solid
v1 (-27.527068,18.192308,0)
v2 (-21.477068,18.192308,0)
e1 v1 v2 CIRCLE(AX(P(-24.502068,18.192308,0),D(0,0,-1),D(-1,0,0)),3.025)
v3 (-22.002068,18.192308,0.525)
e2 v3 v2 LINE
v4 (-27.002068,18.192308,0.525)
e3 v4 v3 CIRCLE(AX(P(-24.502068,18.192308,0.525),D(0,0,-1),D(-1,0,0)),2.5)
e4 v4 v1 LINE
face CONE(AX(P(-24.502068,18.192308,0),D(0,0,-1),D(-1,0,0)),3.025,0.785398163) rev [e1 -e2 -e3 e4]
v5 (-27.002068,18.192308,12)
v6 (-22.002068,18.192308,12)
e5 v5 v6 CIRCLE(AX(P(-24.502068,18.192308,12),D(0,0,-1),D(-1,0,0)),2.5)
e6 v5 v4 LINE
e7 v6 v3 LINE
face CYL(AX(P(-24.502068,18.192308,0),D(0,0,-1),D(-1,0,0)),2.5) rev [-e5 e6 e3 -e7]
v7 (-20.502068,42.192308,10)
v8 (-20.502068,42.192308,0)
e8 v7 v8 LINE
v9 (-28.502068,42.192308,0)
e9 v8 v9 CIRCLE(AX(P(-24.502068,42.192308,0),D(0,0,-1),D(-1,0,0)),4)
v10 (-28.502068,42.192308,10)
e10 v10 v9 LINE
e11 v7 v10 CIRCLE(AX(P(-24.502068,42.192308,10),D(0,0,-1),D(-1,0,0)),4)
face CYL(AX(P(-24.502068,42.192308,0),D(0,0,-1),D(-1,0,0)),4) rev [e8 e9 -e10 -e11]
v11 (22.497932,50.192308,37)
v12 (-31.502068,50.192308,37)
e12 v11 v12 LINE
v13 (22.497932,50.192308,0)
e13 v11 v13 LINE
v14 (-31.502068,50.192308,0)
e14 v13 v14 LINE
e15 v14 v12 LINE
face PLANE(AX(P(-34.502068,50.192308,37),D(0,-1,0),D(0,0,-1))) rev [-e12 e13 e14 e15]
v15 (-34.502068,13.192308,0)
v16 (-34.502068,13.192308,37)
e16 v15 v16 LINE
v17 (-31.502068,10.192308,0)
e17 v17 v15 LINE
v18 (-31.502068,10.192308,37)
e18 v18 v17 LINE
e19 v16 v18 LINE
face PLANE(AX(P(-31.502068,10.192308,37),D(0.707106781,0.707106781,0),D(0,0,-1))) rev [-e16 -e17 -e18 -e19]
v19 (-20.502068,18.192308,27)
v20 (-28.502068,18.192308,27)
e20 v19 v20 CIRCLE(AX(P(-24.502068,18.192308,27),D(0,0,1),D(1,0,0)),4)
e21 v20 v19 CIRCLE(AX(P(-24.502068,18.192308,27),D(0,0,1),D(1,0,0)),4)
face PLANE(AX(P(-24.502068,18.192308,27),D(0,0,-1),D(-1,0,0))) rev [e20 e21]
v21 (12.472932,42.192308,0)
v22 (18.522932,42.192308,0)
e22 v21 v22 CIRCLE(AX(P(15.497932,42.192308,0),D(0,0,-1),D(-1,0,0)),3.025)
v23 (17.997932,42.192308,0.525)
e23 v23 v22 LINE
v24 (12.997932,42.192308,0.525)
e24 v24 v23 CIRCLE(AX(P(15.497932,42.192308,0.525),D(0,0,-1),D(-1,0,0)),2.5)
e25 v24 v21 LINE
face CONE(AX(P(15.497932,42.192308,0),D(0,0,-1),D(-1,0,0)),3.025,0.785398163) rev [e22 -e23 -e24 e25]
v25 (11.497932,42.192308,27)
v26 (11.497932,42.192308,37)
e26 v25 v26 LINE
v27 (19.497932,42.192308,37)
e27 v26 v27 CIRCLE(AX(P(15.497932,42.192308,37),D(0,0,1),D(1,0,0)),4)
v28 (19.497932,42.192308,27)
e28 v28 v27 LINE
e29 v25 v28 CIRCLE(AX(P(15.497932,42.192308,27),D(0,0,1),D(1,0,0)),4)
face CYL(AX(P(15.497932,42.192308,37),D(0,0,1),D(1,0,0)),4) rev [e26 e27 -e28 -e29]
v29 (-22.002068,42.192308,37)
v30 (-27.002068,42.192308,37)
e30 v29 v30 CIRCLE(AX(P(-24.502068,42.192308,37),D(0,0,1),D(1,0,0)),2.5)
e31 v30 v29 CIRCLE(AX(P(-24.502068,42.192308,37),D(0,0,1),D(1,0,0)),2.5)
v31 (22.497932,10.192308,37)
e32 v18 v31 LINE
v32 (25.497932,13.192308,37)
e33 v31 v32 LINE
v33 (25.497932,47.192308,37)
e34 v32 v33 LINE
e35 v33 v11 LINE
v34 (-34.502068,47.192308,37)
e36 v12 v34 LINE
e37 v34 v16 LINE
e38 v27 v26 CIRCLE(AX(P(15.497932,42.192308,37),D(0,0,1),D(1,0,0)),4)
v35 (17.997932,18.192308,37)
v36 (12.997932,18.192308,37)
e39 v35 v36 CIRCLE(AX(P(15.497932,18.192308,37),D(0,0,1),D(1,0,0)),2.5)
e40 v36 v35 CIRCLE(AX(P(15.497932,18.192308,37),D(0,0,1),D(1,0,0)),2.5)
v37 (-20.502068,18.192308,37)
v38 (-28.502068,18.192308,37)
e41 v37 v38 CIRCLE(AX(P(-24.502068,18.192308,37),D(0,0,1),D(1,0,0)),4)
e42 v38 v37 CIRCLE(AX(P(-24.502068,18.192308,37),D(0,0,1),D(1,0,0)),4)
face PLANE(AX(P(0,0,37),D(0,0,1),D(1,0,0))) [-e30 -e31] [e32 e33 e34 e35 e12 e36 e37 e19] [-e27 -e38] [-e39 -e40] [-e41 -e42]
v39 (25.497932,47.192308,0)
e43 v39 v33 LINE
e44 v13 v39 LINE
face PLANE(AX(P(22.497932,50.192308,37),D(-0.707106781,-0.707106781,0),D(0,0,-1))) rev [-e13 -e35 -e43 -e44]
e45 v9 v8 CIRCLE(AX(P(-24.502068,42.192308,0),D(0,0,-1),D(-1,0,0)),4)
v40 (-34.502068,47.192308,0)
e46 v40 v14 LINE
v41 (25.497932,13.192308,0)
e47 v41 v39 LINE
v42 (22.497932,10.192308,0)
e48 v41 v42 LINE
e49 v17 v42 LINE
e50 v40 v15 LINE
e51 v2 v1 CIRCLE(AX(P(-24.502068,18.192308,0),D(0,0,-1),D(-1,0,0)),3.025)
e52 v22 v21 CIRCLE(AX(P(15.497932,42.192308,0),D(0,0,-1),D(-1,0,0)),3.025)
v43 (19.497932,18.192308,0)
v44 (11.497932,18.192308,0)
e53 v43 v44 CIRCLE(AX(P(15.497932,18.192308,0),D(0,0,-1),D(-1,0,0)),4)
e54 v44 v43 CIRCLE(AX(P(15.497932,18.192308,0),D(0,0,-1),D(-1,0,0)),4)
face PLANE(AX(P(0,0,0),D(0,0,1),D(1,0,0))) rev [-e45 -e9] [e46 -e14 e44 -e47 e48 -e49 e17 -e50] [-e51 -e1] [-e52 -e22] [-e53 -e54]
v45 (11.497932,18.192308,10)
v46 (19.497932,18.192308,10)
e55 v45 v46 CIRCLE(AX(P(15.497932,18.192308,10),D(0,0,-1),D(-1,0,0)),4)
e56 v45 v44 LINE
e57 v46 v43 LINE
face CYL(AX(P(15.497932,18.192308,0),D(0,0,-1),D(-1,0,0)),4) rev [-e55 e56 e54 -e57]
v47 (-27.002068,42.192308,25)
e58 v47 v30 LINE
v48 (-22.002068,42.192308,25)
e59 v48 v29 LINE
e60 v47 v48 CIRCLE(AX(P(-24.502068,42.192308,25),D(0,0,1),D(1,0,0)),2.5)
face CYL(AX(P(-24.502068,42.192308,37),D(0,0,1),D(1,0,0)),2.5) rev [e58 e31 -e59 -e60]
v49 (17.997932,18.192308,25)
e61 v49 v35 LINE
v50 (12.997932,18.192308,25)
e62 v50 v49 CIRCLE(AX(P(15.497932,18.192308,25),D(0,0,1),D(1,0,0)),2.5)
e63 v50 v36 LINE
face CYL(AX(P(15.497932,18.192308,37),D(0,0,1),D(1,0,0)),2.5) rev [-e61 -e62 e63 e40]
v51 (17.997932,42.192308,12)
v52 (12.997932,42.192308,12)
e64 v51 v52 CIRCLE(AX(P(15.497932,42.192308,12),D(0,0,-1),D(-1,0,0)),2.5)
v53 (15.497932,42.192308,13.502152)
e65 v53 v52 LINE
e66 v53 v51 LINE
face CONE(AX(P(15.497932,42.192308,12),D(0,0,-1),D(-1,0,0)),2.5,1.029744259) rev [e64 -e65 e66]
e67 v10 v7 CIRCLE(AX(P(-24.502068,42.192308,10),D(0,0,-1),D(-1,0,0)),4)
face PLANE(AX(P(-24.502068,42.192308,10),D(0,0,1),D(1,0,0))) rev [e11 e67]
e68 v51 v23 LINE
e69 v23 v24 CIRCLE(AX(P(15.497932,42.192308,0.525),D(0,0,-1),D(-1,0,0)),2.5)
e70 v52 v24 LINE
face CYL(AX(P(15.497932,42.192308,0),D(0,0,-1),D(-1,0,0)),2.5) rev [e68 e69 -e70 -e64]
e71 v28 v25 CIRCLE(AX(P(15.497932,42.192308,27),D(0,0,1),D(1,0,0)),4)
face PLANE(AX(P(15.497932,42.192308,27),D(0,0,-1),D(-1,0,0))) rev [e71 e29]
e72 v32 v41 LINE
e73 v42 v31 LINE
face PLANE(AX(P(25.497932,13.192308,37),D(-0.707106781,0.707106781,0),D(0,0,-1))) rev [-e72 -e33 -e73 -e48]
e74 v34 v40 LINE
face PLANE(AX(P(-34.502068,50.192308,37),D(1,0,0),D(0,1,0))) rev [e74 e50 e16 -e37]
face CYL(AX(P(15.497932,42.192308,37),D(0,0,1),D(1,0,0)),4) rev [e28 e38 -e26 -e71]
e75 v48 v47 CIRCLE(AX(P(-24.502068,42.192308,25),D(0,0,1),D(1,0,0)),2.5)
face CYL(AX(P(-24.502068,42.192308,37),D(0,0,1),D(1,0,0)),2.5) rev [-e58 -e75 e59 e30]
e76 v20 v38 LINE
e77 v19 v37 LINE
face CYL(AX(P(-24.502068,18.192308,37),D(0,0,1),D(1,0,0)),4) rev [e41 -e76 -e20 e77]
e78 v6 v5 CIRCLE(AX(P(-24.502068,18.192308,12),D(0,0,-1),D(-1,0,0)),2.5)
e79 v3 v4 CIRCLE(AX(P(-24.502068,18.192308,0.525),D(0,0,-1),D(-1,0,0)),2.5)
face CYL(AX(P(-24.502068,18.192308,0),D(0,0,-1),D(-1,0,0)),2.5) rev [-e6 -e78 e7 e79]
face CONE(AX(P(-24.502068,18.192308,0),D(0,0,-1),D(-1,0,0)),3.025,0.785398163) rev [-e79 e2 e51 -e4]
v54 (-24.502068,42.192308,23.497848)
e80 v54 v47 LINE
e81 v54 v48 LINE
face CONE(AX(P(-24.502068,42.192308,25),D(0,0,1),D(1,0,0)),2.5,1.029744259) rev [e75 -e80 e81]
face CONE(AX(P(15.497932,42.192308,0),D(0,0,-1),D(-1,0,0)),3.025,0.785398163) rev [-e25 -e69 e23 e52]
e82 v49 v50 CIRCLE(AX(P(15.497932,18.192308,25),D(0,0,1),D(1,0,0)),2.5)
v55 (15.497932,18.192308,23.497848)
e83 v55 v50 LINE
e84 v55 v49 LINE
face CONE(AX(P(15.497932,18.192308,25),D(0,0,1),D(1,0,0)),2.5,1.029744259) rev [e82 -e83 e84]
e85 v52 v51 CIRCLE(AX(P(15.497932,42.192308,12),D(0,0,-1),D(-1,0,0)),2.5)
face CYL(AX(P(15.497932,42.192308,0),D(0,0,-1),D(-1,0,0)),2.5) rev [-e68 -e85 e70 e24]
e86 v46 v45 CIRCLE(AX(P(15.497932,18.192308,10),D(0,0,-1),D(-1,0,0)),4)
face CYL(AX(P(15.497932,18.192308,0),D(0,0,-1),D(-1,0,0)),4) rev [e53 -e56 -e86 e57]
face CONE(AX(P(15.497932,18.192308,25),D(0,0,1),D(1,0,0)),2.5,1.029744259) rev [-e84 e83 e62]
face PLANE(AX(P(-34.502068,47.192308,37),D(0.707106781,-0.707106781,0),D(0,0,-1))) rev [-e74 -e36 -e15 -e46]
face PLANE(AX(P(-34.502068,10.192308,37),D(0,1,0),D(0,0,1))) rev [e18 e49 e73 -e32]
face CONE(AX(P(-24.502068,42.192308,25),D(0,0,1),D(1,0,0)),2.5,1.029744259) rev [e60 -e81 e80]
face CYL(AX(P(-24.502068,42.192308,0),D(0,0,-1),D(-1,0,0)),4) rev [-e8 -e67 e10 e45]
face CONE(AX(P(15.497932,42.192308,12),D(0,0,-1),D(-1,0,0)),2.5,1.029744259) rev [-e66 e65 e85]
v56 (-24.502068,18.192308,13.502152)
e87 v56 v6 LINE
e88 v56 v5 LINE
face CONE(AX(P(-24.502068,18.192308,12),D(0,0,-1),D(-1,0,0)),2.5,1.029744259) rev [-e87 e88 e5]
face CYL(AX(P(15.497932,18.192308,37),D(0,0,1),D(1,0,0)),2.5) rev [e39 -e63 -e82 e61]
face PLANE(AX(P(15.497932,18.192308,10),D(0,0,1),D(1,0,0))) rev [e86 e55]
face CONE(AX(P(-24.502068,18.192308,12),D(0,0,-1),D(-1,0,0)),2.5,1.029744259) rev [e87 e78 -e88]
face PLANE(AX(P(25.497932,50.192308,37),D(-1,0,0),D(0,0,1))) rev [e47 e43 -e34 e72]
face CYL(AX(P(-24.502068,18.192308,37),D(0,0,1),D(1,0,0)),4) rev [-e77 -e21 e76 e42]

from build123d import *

# Parameters (mm, degrees)
SKETCH1_W                   = 60
SKETCH1_H                   = 40
BOSS_EXTRUDE1_DEPTH         = 37
CHAMFER1_SIZE               = 3
M6_TAPPED_HOLE1_D           = 5
M6_TAPPED_HOLE1_DEPTH       = 12
M6_TAPPED_HOLE1_TIP         = 1.502151548
HOLE1_D                     = 8
HOLE1_DEPTH                 = 10
HOLE2_D                     = 8
HOLE2_DEPTH                 = 10
M6_TAPPED_HOLE2_D           = 5
M6_TAPPED_HOLE2_DEPTH       = 12
M6_TAPPED_HOLE2_CSINK_D     = 6.05
M6_TAPPED_HOLE2_CSINK_ANGLE = 90
M6_TAPPED_HOLE2_TIP         = 1.502151548


with BuildPart() as part:
    # Sketch1 → Boss-Extrude1 (new body)
    with BuildSketch(Plane.XY):
        with Locations((-4.502067899, 30.192307692)):
            Rectangle(SKETCH1_W, SKETCH1_H)
    extrude(amount=BOSS_EXTRUDE1_DEPTH)

    # Chamfer1
    chamfer1_edges = [part.edges().sort_by_distance(p)[0] for p in [
        (-34.502067899, 50.192307692, 18.5),
        (25.497932101, 50.192307692, 18.5),
        (25.497932101, 10.192307692, 18.5),
        (-34.502067899, 10.192307692, 18.5),
    ]]
    chamfer(chamfer1_edges, length=CHAMFER1_SIZE)

    # M6 Tapped Hole1
    with Locations(Plane.XY.offset(37)):
        with Locations((-24.502067899, 42.192307692), (15.497932101, 18.192307692)):
            Hole(M6_TAPPED_HOLE1_D / 2, depth=M6_TAPPED_HOLE1_DEPTH)
            with Locations((0, 0, -(M6_TAPPED_HOLE1_DEPTH + M6_TAPPED_HOLE1_TIP / 2))):  # 118° drill point
                Cone(0, M6_TAPPED_HOLE1_D / 2, M6_TAPPED_HOLE1_TIP, mode=Mode.SUBTRACT)

    # Hole1
    with Locations(Plane.XY.offset(37)):
        with Locations((15.497932101, 42.192307692), (-24.502067899, 18.192307692)):
            Hole(HOLE1_D / 2, depth=HOLE1_DEPTH)

    # Hole2
    with Locations(Plane(origin=(0, 0, 0), x_dir=(-1, 0, 0), z_dir=(0, 0, -1))):
        with Locations((24.502067899, 42.192307692), (-15.497932101, 18.192307692)):
            Hole(HOLE2_D / 2, depth=HOLE2_DEPTH)

    # M6 Tapped Hole2
    with Locations(Plane(origin=(0, 0, 0), x_dir=(-1, 0, 0), z_dir=(0, 0, -1))):
        with Locations((-15.497932101, 42.192307692), (24.502067899, 18.192307692)):
            CounterSinkHole(M6_TAPPED_HOLE2_D / 2, M6_TAPPED_HOLE2_CSINK_D / 2, depth=M6_TAPPED_HOLE2_DEPTH, counter_sink_angle=M6_TAPPED_HOLE2_CSINK_ANGLE)
            with Locations((0, 0, -(M6_TAPPED_HOLE2_DEPTH + M6_TAPPED_HOLE2_TIP / 2))):  # 118° drill point
                Cone(0, M6_TAPPED_HOLE2_D / 2, M6_TAPPED_HOLE2_TIP, mode=Mode.SUBTRACT)


solid = part.part
